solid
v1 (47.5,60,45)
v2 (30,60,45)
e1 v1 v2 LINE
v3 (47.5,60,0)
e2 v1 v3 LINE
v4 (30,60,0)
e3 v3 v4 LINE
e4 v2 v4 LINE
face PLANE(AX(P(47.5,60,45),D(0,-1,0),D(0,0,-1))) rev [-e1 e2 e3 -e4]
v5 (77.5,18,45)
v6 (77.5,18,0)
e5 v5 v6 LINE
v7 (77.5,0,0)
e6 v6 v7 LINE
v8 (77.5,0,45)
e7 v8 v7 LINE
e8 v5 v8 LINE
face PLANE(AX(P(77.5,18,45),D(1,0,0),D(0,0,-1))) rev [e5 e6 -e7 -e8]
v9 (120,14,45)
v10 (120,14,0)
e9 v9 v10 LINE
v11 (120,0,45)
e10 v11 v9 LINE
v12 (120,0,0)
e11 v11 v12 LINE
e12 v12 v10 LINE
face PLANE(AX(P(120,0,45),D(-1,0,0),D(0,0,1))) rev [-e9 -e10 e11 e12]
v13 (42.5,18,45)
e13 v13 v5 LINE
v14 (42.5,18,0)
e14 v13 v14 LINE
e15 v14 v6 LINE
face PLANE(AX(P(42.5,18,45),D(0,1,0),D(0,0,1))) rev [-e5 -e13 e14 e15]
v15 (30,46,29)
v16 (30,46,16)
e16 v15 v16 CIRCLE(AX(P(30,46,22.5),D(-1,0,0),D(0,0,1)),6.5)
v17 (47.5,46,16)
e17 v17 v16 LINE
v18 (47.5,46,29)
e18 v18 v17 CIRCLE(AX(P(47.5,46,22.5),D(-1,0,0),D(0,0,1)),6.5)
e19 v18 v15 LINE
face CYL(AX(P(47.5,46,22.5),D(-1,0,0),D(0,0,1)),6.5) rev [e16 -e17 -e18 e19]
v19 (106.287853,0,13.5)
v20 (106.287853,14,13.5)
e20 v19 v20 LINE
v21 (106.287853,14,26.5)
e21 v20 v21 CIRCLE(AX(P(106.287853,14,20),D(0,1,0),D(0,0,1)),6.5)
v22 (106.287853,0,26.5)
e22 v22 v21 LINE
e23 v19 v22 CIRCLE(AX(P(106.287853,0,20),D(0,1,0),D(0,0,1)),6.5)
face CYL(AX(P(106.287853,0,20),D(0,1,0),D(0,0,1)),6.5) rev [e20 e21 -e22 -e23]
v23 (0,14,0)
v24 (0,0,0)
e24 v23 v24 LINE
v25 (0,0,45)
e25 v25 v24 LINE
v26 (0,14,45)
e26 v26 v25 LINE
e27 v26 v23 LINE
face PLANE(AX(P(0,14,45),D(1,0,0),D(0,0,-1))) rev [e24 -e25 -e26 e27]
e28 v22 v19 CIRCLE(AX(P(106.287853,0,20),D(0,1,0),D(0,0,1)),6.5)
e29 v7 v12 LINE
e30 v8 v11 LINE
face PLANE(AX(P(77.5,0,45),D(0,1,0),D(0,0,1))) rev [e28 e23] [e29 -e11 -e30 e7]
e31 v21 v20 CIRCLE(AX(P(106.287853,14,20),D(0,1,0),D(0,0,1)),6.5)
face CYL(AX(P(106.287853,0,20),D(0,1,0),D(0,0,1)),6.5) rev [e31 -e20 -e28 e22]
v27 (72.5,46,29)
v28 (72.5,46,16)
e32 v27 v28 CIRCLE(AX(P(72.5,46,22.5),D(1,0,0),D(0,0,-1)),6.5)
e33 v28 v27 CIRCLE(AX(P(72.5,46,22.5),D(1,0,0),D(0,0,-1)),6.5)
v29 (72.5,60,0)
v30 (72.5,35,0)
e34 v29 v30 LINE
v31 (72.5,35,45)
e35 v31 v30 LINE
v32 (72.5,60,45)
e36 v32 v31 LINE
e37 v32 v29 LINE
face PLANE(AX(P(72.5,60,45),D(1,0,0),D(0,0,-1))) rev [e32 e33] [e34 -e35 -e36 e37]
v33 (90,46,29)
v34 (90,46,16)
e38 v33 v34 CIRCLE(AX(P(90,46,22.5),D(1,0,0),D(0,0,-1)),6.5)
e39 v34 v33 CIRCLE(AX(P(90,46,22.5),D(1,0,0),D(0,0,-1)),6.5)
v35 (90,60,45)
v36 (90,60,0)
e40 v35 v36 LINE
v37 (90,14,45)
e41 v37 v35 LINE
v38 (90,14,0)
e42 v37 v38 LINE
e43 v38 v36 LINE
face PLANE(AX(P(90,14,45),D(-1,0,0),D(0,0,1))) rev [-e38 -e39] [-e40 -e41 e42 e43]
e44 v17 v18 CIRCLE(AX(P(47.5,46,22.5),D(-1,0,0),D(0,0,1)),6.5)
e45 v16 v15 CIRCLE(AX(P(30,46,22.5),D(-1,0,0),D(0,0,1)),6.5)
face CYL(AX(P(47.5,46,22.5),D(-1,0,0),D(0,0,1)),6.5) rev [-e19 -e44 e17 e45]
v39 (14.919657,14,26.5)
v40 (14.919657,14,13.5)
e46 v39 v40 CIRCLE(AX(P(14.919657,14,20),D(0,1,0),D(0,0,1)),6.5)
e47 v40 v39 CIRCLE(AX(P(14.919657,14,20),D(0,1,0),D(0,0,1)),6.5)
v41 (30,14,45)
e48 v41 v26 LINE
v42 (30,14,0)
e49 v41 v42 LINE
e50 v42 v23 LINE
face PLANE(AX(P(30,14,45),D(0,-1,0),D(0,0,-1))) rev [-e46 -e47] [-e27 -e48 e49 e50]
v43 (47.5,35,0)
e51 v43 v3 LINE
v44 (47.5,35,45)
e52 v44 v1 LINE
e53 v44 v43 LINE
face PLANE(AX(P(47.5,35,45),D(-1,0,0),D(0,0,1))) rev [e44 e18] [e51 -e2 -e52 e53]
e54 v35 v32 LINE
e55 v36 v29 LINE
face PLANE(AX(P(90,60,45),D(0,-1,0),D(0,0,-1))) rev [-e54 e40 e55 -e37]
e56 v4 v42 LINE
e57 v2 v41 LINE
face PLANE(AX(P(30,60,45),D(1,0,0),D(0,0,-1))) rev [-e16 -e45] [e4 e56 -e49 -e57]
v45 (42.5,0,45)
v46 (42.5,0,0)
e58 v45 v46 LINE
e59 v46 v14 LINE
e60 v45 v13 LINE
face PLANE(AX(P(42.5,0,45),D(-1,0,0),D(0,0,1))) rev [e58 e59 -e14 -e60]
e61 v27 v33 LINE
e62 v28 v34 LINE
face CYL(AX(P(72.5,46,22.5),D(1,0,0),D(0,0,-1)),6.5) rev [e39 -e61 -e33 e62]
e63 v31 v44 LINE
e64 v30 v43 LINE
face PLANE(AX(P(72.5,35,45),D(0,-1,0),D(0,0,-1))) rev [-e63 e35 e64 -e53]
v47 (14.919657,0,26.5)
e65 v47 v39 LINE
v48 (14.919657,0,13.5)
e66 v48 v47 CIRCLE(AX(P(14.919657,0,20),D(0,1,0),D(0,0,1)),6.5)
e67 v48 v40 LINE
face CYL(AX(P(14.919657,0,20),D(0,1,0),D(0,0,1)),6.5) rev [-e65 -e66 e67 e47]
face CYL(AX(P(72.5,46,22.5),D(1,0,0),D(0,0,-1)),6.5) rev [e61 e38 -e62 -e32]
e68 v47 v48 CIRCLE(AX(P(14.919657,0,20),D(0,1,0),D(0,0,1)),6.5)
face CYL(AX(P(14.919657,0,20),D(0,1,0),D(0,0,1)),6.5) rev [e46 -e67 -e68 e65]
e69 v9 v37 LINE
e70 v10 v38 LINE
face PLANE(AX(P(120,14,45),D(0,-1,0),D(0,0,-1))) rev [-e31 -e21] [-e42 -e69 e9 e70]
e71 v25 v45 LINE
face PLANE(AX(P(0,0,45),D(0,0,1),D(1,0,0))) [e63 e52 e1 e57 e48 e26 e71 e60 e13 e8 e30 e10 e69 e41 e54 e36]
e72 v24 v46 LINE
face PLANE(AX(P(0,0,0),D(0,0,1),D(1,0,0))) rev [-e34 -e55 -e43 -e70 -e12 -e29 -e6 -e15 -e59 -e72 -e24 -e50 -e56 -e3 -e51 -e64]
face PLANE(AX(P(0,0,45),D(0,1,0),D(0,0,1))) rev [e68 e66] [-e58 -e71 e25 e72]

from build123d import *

# Parameters (mm, degrees)
BRACKET_BODY_DEPTH      = 45
UPRIGHT_HOLE_A_SKETCH_R = 6.5
UPRIGHT_HOLE_A_13_DEPTH = 17.5
UPRIGHT_START           = -17.5
UPRIGHT_HOLE_B_SKETCH_R = 6.5
UPRIGHT_HOLE_B_13_DEPTH = 17.5
FLANGE_HOLE_A_SKETCH_R  = 6.5
FLANGE_HOLE_A_13_DEPTH  = 14
FLANGE_HOLE_B_SKETCH_R  = 6.5
FLANGE_HOLE_B_13_DEPTH  = 14


with BuildPart() as part:
    # Bracket Profile Sketch → Bracket Body (new body)
    with BuildSketch(Plane.XY):
        Polygon((0, 0), (42.5, 0), (42.5, 18), (77.5, 18), (77.5, 0), (120, 0), (120, 14), (90, 14), (90, 60), (72.5, 60), (72.5, 35), (47.5, 35), (47.5, 60), (30, 60), (30, 14), (0, 14), align=None)
    extrude(amount=BRACKET_BODY_DEPTH)

    # Upright Hole A Sketch → Upright Hole A Ø13 (cut)
    with BuildSketch(Plane.ZY.offset(-30)):
        with Locations((22.5, 46)):
            Circle(UPRIGHT_HOLE_A_SKETCH_R)
    extrude(amount=-UPRIGHT_HOLE_A_13_DEPTH, mode=Mode.SUBTRACT)

    # Upright Hole B Sketch → Upright Hole B Ø13 (cut)
    with BuildSketch(Plane(origin=(90, 0, 0), x_dir=(0, 0, -1), z_dir=(1, 0, 0)).offset(UPRIGHT_START)):
        with Locations(Location((-22.5, 46, 0), (0, 0, 180))):
            Circle(UPRIGHT_HOLE_B_SKETCH_R)
    extrude(amount=UPRIGHT_HOLE_B_13_DEPTH, mode=Mode.SUBTRACT)

    # Flange Hole A Sketch → Flange Hole A Ø13 (cut)
    with BuildSketch(Plane(origin=(0, 14, 0), x_dir=(1, 0, 0), z_dir=(0, 1, 0))):
        with Locations(Location((14.919656615, -20, 0), (0, 0, 270))):
            Circle(FLANGE_HOLE_A_SKETCH_R)
    extrude(amount=-FLANGE_HOLE_A_13_DEPTH, mode=Mode.SUBTRACT)

    # Flange Hole B Sketch → Flange Hole B Ø13 (cut)
    with BuildSketch(Plane(origin=(0, 14, 0), x_dir=(1, 0, 0), z_dir=(0, 1, 0))):
        with Locations(Location((106.287852583, -20, 0), (0, 0, 270))):
            Circle(FLANGE_HOLE_B_SKETCH_R)
    extrude(amount=-FLANGE_HOLE_B_13_DEPTH, mode=Mode.SUBTRACT)


solid = part.part
